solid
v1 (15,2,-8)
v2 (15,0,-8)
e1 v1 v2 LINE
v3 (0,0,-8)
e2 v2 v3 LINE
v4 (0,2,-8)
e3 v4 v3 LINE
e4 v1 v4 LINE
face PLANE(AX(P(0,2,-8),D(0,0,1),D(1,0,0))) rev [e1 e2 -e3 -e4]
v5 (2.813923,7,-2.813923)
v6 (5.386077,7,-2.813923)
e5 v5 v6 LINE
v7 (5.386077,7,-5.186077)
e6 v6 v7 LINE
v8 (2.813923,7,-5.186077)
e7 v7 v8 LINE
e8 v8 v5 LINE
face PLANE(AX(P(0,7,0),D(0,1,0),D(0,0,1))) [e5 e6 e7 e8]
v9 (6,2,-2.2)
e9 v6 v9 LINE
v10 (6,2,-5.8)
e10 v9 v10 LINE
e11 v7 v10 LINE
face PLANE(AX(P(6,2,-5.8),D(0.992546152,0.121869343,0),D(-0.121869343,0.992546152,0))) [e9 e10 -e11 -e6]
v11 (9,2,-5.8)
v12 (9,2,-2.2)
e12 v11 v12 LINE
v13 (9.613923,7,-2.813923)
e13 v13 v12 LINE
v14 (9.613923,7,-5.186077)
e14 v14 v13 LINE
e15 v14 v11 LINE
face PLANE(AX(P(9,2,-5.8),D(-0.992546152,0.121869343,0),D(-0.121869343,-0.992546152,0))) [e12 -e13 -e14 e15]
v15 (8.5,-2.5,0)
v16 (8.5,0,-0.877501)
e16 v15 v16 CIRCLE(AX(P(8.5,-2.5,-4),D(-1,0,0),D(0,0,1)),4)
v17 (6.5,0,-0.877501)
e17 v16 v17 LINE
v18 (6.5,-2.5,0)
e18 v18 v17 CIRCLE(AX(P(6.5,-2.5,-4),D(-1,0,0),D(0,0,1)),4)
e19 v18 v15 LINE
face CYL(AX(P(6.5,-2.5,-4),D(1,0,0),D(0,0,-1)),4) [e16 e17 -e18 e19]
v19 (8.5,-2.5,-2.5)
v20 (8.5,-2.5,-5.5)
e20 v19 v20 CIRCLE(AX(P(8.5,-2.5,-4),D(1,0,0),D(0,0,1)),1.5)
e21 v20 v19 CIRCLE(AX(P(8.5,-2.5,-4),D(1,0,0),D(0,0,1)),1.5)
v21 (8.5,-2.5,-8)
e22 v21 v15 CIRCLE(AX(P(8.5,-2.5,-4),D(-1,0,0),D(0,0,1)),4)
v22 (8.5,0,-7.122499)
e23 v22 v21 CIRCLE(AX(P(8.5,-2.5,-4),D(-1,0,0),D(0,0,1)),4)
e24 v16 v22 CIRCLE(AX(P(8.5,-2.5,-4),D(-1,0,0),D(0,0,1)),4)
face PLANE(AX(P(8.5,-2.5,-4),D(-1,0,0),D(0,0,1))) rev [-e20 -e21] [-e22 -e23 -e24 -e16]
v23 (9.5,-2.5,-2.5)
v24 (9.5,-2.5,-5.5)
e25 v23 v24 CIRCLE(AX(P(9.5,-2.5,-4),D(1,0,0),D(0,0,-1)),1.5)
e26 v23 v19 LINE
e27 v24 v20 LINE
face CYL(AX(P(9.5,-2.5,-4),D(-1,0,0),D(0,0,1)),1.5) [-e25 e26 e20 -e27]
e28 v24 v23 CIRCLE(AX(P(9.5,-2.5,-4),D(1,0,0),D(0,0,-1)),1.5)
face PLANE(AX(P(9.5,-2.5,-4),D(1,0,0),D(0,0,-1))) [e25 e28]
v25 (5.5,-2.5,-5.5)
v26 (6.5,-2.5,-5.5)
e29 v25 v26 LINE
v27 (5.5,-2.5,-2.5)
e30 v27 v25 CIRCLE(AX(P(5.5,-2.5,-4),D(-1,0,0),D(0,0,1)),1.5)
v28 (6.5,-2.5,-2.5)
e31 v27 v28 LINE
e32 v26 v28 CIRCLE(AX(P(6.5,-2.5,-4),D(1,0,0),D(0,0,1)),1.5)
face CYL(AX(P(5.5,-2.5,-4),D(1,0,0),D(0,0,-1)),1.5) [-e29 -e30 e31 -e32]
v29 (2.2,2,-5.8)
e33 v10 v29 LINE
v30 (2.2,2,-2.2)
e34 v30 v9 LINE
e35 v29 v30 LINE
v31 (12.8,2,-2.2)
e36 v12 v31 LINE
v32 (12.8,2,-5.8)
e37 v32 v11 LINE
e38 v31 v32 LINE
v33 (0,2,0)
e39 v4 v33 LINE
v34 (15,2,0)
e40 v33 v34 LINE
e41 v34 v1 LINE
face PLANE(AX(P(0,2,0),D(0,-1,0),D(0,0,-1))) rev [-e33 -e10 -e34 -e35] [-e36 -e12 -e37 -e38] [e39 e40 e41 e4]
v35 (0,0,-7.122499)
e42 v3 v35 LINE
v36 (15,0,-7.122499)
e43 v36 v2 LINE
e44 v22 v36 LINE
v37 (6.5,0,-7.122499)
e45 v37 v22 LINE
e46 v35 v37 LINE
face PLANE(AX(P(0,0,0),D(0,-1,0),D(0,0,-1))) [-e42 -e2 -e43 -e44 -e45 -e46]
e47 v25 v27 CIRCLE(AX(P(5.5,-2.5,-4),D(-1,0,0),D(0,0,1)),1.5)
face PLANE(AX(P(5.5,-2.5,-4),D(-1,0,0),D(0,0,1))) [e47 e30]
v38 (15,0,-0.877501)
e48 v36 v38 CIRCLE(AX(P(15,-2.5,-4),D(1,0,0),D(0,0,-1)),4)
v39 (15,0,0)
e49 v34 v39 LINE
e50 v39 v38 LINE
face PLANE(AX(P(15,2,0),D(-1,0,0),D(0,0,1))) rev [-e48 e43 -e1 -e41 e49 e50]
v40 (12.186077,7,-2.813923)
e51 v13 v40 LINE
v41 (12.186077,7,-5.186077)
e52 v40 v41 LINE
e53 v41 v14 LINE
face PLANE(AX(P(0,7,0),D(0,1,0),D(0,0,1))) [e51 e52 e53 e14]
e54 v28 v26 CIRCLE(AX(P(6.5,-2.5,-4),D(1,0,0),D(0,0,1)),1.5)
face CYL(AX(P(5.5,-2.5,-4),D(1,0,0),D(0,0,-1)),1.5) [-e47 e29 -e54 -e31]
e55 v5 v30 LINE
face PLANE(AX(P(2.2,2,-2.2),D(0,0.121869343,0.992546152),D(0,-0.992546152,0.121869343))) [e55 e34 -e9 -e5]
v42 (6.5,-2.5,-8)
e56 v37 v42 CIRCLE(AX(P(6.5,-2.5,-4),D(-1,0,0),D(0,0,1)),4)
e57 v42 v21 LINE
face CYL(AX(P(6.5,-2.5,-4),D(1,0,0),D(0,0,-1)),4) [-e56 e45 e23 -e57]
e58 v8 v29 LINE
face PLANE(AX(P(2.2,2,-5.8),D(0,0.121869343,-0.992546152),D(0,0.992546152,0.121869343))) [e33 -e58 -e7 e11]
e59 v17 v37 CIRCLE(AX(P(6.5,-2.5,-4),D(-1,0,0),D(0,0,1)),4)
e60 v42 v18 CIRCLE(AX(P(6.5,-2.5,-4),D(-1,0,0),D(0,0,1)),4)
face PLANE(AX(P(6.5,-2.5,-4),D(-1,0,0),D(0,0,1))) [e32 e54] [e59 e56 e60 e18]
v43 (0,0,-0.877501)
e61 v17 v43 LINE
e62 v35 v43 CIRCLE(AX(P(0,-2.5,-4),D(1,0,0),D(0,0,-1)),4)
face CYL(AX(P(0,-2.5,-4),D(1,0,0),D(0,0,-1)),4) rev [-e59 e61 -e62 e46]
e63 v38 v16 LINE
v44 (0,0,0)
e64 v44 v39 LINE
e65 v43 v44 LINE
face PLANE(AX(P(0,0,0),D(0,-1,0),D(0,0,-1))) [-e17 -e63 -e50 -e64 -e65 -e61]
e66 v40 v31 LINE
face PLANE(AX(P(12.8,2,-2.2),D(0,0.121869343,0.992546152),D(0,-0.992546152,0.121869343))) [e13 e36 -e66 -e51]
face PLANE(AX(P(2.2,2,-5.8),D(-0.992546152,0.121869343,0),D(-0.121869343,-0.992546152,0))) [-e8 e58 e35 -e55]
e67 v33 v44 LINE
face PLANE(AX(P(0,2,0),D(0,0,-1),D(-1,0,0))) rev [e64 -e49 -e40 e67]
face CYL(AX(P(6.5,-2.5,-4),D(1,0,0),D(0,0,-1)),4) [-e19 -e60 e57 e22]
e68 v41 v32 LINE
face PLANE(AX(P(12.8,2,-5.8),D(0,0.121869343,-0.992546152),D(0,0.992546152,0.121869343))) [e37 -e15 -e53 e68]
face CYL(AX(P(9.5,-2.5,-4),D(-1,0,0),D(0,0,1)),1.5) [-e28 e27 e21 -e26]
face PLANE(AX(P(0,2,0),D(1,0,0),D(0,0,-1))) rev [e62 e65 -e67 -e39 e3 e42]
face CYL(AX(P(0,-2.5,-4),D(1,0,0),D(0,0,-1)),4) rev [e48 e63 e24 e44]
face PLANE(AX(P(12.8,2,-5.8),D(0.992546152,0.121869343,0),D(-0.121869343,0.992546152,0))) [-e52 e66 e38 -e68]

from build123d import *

# Parameters (mm, degrees)
BASE_PLATE_SKETCH_W                    = 15
BASE_PLATE_SKETCH_H                    = 8
BASE_PLATE_15X8X2_DEPTH                = 2
HIP_BLOCKS_SKETCH_W                    = 3.8
HIP_BLOCKS_SKETCH_H                    = 3.6
HIP_BLOCKS_DRAFTED_5MM_DEPTH           = 5
HIP_BLOCKS_DRAFTED_5MM_DRAFT           = 7
HIP_BLOCKS_DRAFTED_5MM_PROFILE_2_DEPTH = 5
HIP_BLOCKS_DRAFTED_5MM_PROFILE_2_DRAFT = 7
UNDERSIDE_RELIEF_SKETCH_R              = 4
UNDERSIDE_RELIEF_CUT_DEPTH             = 19.384776311
HIP_DISC_SKETCH_R                      = 4
HIP_DISC_8_DEPTH                       = 1
AXLE_PIN_A_SKETCH_R                    = 1.5
AXLE_PIN_A_3_DEPTH                     = 1
AXLE_PIN_B_SKETCH_R                    = 1.5
AXLE_PIN_B_3_DEPTH                     = 1


with BuildPart() as part:
    # Base Plate Sketch → Base Plate 15x8x2 (new body)
    with BuildSketch(Plane(origin=(0, 0, 0), x_dir=(1, 0, 0), z_dir=(0, 1, 0))):
        with Locations((7.5, 4)):
            Rectangle(BASE_PLATE_SKETCH_W, BASE_PLATE_SKETCH_H)
    extrude(amount=BASE_PLATE_15X8X2_DEPTH)


with BuildPart() as hip_blocks_drafted_5mm_tool:
    # Hip Blocks Sketch → Hip Blocks Drafted 5mm (with draft: the straight prism first)
    with BuildSketch(Plane(origin=(0, 2, 0), x_dir=(1, 0, 0), z_dir=(0, 1, 0))):
        with Locations((4.1, 4)):
            Rectangle(HIP_BLOCKS_SKETCH_W, HIP_BLOCKS_SKETCH_H)
    extrude(amount=HIP_BLOCKS_DRAFTED_5MM_DEPTH)
    # Hip Blocks Drafted 5mm: the draft: its side faces are tilted about the plane it starts from
    hip_blocks_drafted_5mm_sides = [hip_blocks_drafted_5mm_tool.faces().sort_by_distance(p)[0] for p in [
        (2.2, 4.5, -4),
        (4.1, 4.5, -2.2),
        (6, 4.5, -4),
        (4.1, 4.5, -5.8),
    ]]
    draft(hip_blocks_drafted_5mm_sides, Plane(origin=(0, 2, 0), x_dir=(1, 0, 0), z_dir=(0, 1, 0)), HIP_BLOCKS_DRAFTED_5MM_DRAFT)


with BuildPart() as part_1:
    add(part.part)

    # Hip Blocks Drafted 5mm: add hip_blocks_drafted_5mm_tool
    add(hip_blocks_drafted_5mm_tool.part)


with BuildPart() as hip_blocks_drafted_5mm_profile_2_tool:
    # Hip Blocks Sketch → Hip Blocks Drafted 5mm profile 2 (with draft: the straight prism first)
    with BuildSketch(Plane(origin=(0, 2, 0), x_dir=(1, 0, 0), z_dir=(0, 1, 0))):
        with Locations((10.9, 4)):
            Rectangle(HIP_BLOCKS_SKETCH_W, HIP_BLOCKS_SKETCH_H)
    extrude(amount=HIP_BLOCKS_DRAFTED_5MM_PROFILE_2_DEPTH)
    # Hip Blocks Drafted 5mm profile 2: the draft: its side faces are tilted about the plane it starts from
    hip_blocks_drafted_5mm_profile_2_sides = [hip_blocks_drafted_5mm_profile_2_tool.faces().sort_by_distance(p)[0] for p in [
        (10.9, 4.5, -5.8),
        (9, 4.5, -4),
        (10.9, 4.5, -2.2),
        (12.8, 4.5, -4),
    ]]
    draft(hip_blocks_drafted_5mm_profile_2_sides, Plane(origin=(0, 2, 0), x_dir=(1, 0, 0), z_dir=(0, 1, 0)), HIP_BLOCKS_DRAFTED_5MM_PROFILE_2_DRAFT)


with BuildPart() as part_2:
    add(part_1.part)

    # Hip Blocks Drafted 5mm profile 2: add hip_blocks_drafted_5mm_profile_2_tool
    add(hip_blocks_drafted_5mm_profile_2_tool.part)

    # Underside Relief Sketch → Underside Relief Cut (cut, through all)
    with BuildSketch(Plane(origin=(15, 0, 0), x_dir=(0, 0, -1), z_dir=(1, 0, 0))):
        with Locations((4, -2.5)):
            Circle(UNDERSIDE_RELIEF_SKETCH_R)
    extrude(amount=-UNDERSIDE_RELIEF_CUT_DEPTH, mode=Mode.SUBTRACT)

    # Hip Disc Sketch → Hip Disc Ø8 (add, symmetric)
    with BuildSketch(Plane.ZY.offset(-7.5)):
        with Locations((-4, -2.5)):
            Circle(HIP_DISC_SKETCH_R)
    extrude(amount=HIP_DISC_8_DEPTH, both=True)

    # Axle Pin A Sketch → Axle Pin A Ø3 (add, symmetric)
    with BuildSketch(Plane(origin=(8.5, 0, 0), x_dir=(0, 0, -1), z_dir=(1, 0, 0))):
        with Locations(Location((4, -2.5, 0), (0, 0, 180))):
            Circle(AXLE_PIN_A_SKETCH_R)
    extrude(amount=AXLE_PIN_A_3_DEPTH, both=True)

    # Axle Pin B Sketch → Axle Pin B Ø3 (add, symmetric)
    with BuildSketch(Plane.ZY.offset(-6.5)):
        with Locations((-4, -2.5)):
            Circle(AXLE_PIN_B_SKETCH_R)
    extrude(amount=AXLE_PIN_B_3_DEPTH, both=True)


solid = part_2.part
